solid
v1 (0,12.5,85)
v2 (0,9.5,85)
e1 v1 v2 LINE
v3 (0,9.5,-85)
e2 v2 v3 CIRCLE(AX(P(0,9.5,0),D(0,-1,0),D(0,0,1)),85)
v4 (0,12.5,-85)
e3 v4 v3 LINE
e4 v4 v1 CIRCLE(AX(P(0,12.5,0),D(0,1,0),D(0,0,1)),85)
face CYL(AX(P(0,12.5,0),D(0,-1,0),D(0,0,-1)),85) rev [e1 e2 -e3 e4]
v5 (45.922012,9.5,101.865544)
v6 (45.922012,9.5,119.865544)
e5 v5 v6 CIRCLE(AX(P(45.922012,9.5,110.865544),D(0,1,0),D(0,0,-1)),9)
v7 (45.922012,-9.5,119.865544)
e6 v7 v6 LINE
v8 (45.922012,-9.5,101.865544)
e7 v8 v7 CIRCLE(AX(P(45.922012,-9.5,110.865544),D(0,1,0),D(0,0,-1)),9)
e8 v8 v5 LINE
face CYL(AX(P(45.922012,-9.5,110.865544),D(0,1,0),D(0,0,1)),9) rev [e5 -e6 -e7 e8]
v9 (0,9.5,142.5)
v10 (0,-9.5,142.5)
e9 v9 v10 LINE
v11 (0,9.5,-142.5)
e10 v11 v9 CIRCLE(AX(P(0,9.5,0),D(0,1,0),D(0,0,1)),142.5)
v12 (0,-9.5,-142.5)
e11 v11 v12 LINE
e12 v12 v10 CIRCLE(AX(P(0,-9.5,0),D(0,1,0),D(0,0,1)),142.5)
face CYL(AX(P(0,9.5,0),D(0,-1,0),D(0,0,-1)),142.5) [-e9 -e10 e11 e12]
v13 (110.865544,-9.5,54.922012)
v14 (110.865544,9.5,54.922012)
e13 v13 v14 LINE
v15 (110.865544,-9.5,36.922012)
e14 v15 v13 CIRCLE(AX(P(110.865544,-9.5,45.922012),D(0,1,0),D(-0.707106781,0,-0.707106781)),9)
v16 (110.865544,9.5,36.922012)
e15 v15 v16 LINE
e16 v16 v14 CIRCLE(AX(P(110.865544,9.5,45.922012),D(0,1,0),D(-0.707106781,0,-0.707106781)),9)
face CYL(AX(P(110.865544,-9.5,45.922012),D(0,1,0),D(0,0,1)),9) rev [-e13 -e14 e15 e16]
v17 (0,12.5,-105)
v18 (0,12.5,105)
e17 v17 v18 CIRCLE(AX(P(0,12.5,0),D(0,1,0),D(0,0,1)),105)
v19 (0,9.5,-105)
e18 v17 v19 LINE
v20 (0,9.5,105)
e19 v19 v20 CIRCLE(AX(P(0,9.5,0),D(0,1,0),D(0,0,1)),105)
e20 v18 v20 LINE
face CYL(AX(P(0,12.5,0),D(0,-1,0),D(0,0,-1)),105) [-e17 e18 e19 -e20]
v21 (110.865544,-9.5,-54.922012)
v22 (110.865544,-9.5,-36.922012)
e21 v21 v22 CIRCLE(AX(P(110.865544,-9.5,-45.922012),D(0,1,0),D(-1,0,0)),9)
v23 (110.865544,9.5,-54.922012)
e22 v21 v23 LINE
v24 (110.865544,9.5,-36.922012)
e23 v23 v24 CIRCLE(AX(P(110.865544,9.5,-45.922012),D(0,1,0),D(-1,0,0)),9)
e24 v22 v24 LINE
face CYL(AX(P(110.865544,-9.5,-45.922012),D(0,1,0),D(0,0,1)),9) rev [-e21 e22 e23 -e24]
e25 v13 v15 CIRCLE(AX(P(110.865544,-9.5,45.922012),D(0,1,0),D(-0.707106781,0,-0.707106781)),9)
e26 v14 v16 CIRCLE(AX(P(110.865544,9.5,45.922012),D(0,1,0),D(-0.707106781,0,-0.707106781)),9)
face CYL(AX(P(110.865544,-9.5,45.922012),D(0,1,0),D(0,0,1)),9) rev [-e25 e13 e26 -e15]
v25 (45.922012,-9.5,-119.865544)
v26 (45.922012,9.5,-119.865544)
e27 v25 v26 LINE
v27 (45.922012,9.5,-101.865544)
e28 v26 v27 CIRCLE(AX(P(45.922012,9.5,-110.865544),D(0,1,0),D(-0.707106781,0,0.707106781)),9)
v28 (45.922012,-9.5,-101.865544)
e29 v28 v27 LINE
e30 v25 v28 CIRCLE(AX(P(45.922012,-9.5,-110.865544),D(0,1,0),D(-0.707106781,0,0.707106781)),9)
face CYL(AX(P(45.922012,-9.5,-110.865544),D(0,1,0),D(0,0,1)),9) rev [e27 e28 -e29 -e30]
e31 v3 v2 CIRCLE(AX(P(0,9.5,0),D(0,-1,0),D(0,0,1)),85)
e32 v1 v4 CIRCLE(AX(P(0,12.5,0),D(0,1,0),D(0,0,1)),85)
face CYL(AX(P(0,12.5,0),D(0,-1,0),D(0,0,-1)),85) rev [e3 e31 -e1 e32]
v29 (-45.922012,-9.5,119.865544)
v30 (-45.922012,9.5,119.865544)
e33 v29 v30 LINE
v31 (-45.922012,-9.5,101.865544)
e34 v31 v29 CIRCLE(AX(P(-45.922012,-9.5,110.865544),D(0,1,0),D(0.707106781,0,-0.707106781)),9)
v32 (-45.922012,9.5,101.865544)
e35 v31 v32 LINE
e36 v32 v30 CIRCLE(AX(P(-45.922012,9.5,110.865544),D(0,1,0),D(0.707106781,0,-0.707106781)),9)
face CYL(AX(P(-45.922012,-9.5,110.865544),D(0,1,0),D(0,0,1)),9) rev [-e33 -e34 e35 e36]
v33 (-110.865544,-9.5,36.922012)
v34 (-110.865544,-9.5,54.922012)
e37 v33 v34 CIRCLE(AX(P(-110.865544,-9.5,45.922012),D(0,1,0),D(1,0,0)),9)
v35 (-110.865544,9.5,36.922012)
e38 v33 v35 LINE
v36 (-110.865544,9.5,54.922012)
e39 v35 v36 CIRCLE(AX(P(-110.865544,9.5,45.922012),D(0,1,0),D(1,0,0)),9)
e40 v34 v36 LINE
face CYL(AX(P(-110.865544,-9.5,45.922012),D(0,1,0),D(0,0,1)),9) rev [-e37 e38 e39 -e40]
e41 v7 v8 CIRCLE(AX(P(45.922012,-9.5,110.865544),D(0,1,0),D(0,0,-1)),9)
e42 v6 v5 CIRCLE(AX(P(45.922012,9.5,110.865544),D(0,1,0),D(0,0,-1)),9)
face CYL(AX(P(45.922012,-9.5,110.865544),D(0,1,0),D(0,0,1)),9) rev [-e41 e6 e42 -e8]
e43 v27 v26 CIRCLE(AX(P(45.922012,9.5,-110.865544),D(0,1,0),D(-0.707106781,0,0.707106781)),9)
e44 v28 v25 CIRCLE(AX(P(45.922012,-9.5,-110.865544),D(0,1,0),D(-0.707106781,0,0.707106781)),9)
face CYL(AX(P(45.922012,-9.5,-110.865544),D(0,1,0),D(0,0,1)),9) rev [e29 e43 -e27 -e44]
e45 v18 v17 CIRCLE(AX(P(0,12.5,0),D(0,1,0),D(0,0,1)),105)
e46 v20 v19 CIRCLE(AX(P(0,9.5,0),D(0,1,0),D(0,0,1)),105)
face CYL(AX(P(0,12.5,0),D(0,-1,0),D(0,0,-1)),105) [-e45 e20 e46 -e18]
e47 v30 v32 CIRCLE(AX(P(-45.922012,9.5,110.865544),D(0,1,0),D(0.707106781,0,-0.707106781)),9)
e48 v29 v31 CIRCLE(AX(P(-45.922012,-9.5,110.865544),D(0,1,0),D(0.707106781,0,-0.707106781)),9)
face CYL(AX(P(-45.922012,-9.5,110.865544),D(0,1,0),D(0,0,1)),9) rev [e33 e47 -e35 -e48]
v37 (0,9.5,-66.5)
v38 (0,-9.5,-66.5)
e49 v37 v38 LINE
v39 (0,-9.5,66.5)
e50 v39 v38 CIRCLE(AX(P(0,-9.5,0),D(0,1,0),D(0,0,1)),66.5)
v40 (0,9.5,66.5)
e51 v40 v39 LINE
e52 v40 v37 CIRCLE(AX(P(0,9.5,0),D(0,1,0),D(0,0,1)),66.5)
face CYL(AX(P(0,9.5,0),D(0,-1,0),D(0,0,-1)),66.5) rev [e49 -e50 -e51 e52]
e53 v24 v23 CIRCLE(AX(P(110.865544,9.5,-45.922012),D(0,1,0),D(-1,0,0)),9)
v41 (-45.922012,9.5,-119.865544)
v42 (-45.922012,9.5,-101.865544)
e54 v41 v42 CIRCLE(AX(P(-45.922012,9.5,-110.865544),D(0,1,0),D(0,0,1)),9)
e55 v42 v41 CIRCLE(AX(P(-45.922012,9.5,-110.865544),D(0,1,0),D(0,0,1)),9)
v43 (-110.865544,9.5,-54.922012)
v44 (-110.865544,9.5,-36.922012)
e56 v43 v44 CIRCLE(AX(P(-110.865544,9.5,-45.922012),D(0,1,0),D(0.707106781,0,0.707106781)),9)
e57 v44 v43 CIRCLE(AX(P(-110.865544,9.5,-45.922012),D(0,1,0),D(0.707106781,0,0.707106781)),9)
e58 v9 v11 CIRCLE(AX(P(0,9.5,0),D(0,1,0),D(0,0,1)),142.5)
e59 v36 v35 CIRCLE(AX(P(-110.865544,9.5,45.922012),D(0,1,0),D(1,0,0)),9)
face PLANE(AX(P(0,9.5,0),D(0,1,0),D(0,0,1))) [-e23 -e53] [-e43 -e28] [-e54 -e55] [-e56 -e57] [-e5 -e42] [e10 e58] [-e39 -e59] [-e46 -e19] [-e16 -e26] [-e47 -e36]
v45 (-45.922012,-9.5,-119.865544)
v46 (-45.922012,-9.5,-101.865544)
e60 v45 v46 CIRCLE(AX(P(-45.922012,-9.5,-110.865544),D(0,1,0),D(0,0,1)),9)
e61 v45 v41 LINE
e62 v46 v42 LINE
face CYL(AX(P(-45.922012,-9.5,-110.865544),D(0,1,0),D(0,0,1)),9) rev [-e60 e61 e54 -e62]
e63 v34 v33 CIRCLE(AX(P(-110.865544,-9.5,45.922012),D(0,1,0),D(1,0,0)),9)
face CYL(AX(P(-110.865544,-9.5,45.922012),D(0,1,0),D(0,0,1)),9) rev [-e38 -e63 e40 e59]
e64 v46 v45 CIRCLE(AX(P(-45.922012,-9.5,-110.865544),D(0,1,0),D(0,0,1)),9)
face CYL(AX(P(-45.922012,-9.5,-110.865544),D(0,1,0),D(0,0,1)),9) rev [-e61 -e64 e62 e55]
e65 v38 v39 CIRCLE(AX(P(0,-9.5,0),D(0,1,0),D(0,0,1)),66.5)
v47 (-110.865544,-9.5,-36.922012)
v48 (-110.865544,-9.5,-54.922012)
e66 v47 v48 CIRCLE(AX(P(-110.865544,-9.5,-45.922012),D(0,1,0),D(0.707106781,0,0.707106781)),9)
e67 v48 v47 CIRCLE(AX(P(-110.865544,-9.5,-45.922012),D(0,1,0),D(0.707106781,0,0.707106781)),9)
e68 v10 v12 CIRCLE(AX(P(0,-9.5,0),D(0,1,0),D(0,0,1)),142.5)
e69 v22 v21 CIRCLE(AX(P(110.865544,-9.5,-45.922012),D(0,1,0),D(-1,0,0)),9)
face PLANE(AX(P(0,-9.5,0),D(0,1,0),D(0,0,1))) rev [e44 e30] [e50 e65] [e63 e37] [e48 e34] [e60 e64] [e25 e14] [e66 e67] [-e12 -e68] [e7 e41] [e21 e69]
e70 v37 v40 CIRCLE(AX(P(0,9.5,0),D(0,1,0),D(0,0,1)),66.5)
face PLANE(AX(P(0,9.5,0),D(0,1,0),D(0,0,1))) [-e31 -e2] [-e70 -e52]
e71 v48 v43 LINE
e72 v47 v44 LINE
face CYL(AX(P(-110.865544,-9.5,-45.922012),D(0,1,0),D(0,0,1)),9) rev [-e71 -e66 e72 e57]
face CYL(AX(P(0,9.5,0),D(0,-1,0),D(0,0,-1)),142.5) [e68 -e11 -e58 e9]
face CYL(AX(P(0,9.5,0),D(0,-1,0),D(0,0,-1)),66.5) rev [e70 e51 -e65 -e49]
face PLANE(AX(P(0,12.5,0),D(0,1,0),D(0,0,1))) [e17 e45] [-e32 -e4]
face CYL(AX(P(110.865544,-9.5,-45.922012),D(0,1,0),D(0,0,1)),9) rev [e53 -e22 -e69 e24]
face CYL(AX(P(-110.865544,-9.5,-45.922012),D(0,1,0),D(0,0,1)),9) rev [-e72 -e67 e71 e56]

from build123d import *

# Parameters (mm, degrees)
SKETCH1_R           = 142.5
SKETCH1_R_2         = 66.5
BOSS_EXTRUDE1_DEPTH = 9.5
SKETCH2_R           = 105
SKETCH2_R_2         = 85
BOSS_EXTRUDE2_DEPTH = 3
SKETCH3_R           = 9
CUT_EXTRUDE1_DEPTH  = 203.41911965
CIRPATTERN1_COUNT   = 8


with BuildPart() as part:
    # Sketch1 → Boss-Extrude1 (new, symmetric)
    with BuildSketch(Plane(origin=(0, 0, 0), x_dir=(1, 0, 0), z_dir=(0, 1, 0))):
        with Locations(Location((0, 0, 0), (0, 0, 270))):
            Circle(SKETCH1_R)
        with Locations(Location((0, 0, 0), (0, 0, 270))):
            Circle(SKETCH1_R_2, mode=Mode.SUBTRACT)
    extrude(amount=BOSS_EXTRUDE1_DEPTH, both=True)

    # Sketch2 → Boss-Extrude2 (add)
    with BuildSketch(Plane(origin=(0, 9.5, 0), x_dir=(1, 0, 0), z_dir=(0, 1, 0))):
        with Locations(Location((0, 0, 0), (0, 0, 270))):
            Circle(SKETCH2_R)
        with Locations(Location((0, 0, 0), (0, 0, 270))):
            Circle(SKETCH2_R_2, mode=Mode.SUBTRACT)
    extrude(amount=BOSS_EXTRUDE2_DEPTH)

    # Sketch3 → Cut-Extrude1 (cut, through all)
    with BuildSketch(Plane(origin=(0, 9.5, 0), x_dir=(1, 0, 0), z_dir=(0, 1, 0))):
        with Locations(Location((-45.922011884, 110.865543901, 0), (0, 0, 270))):
            Circle(SKETCH3_R)
    cut_extrude1 = extrude(amount=-CUT_EXTRUDE1_DEPTH, mode=Mode.SUBTRACT)

    # CirPattern1: Cut-Extrude1 ×8 about axis
    cirpattern1_axis = Axis((0, 0, 0), (0, 1, 0))
    for i in range(1, CIRPATTERN1_COUNT):
        add(cut_extrude1.rotate(cirpattern1_axis, i * 360 / CIRPATTERN1_COUNT), mode=Mode.SUBTRACT)


solid = part.part
